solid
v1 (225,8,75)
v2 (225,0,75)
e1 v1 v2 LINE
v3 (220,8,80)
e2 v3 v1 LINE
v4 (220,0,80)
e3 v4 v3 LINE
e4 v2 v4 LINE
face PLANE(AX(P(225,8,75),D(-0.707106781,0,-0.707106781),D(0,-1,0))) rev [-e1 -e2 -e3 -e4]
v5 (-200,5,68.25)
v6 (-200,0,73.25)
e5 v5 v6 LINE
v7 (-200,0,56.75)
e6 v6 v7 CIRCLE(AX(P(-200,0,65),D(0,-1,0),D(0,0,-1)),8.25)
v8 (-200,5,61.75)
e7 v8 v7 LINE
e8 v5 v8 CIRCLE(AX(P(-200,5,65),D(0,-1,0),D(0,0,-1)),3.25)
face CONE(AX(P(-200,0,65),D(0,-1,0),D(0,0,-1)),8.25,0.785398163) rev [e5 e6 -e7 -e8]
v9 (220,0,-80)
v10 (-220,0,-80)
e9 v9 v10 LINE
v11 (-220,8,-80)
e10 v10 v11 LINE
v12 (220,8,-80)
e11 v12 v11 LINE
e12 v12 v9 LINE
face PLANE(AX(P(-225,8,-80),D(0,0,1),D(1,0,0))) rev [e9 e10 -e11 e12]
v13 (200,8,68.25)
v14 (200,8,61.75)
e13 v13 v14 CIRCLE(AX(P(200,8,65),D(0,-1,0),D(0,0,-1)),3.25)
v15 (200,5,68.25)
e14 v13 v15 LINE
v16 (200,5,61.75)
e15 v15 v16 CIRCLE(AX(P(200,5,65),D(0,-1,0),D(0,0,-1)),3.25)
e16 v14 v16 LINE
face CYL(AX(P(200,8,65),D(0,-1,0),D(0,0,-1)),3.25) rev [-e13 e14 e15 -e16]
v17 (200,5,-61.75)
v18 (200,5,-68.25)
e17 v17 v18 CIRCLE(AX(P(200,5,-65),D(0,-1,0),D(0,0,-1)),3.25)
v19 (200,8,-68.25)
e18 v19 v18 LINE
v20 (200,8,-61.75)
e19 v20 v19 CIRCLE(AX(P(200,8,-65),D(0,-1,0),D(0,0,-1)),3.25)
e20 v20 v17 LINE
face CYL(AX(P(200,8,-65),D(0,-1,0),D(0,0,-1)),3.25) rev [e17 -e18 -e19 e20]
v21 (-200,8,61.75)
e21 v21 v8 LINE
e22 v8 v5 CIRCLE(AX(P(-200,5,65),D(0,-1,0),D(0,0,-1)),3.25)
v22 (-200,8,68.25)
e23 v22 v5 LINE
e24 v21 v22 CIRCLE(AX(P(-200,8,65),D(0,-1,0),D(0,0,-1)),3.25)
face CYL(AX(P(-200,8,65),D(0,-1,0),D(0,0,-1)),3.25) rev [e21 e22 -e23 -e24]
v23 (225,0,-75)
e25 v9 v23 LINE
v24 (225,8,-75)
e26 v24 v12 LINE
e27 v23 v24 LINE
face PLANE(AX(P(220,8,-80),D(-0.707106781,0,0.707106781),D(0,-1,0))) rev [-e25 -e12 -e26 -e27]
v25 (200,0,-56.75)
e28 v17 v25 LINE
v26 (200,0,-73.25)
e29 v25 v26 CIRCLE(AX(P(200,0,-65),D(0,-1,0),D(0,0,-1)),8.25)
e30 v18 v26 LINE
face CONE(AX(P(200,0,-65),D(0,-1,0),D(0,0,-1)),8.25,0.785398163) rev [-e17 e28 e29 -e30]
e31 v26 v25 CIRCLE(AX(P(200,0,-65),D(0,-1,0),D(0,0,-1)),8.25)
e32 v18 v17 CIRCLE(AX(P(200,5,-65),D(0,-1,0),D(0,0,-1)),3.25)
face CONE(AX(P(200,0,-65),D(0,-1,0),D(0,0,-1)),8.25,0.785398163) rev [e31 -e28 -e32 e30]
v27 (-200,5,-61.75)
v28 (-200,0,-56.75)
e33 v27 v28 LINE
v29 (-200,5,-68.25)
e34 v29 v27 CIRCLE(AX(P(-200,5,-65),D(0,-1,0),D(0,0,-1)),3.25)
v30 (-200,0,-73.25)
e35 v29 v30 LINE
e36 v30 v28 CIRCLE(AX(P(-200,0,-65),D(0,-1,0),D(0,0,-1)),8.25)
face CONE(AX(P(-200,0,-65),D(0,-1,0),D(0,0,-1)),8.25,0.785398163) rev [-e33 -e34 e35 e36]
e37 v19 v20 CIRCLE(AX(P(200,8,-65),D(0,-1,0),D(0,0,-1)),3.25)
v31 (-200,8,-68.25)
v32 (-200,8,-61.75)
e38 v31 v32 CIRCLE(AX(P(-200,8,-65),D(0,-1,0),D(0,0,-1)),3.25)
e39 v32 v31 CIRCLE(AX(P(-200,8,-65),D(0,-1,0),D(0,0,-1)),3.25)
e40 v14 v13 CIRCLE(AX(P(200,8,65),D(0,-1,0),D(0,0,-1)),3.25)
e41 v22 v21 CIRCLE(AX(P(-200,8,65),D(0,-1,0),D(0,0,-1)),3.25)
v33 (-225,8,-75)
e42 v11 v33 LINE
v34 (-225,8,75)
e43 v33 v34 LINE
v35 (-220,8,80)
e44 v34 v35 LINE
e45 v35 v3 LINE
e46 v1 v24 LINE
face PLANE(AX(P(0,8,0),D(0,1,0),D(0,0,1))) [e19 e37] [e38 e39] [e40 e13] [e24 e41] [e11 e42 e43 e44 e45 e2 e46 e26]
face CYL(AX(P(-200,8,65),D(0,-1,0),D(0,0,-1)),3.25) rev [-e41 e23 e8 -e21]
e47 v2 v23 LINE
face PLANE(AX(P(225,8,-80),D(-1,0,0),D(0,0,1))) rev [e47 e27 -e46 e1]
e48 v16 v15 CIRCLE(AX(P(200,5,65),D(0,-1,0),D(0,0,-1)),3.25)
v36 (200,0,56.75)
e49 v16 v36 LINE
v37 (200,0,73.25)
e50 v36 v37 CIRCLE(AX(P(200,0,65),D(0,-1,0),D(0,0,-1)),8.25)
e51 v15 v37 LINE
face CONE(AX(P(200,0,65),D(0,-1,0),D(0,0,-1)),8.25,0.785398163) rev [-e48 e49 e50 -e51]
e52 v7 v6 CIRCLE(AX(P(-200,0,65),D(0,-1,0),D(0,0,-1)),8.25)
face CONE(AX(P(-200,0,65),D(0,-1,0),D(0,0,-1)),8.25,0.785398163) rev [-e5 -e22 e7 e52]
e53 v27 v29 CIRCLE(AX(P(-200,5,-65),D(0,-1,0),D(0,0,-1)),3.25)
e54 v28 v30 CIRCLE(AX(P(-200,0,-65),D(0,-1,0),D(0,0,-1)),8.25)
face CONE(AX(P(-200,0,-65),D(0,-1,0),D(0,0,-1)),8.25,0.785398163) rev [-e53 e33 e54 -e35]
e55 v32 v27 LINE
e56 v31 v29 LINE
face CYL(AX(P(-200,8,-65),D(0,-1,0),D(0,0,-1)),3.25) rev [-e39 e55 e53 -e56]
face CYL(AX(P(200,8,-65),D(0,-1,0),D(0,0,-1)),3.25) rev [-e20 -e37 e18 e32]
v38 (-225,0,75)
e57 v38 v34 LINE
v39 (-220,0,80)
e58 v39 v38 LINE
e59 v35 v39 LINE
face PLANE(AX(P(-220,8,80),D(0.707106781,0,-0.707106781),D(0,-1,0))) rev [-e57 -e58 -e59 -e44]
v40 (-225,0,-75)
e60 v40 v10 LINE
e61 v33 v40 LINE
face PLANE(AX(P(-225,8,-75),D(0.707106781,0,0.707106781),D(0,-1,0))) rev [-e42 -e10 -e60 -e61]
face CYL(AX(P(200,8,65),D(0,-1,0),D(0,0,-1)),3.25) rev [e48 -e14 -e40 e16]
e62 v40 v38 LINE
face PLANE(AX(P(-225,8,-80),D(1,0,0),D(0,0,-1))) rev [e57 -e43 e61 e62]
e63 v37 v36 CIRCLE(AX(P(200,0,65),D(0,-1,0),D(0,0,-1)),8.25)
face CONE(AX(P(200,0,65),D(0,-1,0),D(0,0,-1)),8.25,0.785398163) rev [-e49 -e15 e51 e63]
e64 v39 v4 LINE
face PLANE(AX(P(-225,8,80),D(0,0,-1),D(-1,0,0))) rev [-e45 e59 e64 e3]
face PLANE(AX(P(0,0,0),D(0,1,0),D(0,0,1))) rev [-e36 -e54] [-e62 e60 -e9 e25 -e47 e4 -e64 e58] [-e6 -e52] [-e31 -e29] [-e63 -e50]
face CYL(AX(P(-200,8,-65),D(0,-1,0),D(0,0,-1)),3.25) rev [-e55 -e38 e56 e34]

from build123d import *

# Parameters (mm, degrees)
SKETCH1_W                    = 450
SKETCH1_H                    = 160
BOSS_EXTRUDE1_DEPTH          = 8
SKETCH15_R                   = 3.25
CUT_EXTRUDE5_DEPTH           = 8
SKETCH16_R                   = 8.25
CUT_EXTRUDE6_DEPTH           = 5
CUT_EXTRUDE6_DRAFT           = -45
CUT_EXTRUDE6_PROFILE_2_DEPTH = 5
CUT_EXTRUDE6_PROFILE_2_DRAFT = -45
CUT_EXTRUDE6_PROFILE_3_DEPTH = 5
CUT_EXTRUDE6_PROFILE_3_DRAFT = -45
CUT_EXTRUDE6_PROFILE_4_DEPTH = 5
CUT_EXTRUDE6_PROFILE_4_DRAFT = -45
CHAMFER1_SIZE                = 5


with BuildPart() as part:
    # Sketch1 → Boss-Extrude1 (new body)
    with BuildSketch(Plane(origin=(0, 0, 0), x_dir=(1, 0, 0), z_dir=(0, 1, 0))):
        Rectangle(SKETCH1_W, SKETCH1_H)
    extrude(amount=BOSS_EXTRUDE1_DEPTH)

    # Sketch15 → Cut-Extrude5 (cut)
    with BuildSketch(Plane.XZ):
        with Locations(Location((-200, 65, 0), (0, 0, 270))):
            Circle(SKETCH15_R)
        with Locations(Location((-200, -65, 0), (0, 0, 270))):
            Circle(SKETCH15_R)
        with Locations(Location((200, 65, 0), (0, 0, 270))):
            Circle(SKETCH15_R)
        with Locations(Location((200, -65, 0), (0, 0, 270))):
            Circle(SKETCH15_R)
    extrude(amount=-CUT_EXTRUDE5_DEPTH, mode=Mode.SUBTRACT)


with BuildPart() as cut_extrude6_tool:
    # Sketch16 → Cut-Extrude6 (with draft: the straight prism first)
    with BuildSketch(Plane.XZ):
        with Locations((-200, 65)):
            Circle(SKETCH16_R)
    extrude(amount=-CUT_EXTRUDE6_DEPTH)
    # Cut-Extrude6: the draft: its side faces are tilted about the plane it starts from
    cut_extrude6_sides = [cut_extrude6_tool.faces().sort_by_distance(p)[0] for p in [
        (-208.25, 2.5, 65),
    ]]
    draft(cut_extrude6_sides, Plane.XZ, CUT_EXTRUDE6_DRAFT)


with BuildPart() as part_1:
    add(part.part)

    # Cut-Extrude6: cut by cut_extrude6_tool
    add(cut_extrude6_tool.part, mode=Mode.SUBTRACT)


with BuildPart() as cut_extrude6_profile_2_tool:
    # Sketch16 → Cut-Extrude6 profile 2 (with draft: the straight prism first)
    with BuildSketch(Plane.XZ):
        with Locations((-200, -65)):
            Circle(SKETCH16_R)
    extrude(amount=-CUT_EXTRUDE6_PROFILE_2_DEPTH)
    # Cut-Extrude6 profile 2: the draft: its side faces are tilted about the plane it starts from
    cut_extrude6_profile_2_sides = [cut_extrude6_profile_2_tool.faces().sort_by_distance(p)[0] for p in [
        (-208.25, 2.5, -65),
    ]]
    draft(cut_extrude6_profile_2_sides, Plane.XZ, CUT_EXTRUDE6_PROFILE_2_DRAFT)


with BuildPart() as part_2:
    add(part_1.part)

    # Cut-Extrude6 profile 2: cut by cut_extrude6_profile_2_tool
    add(cut_extrude6_profile_2_tool.part, mode=Mode.SUBTRACT)


with BuildPart() as cut_extrude6_profile_3_tool:
    # Sketch16 → Cut-Extrude6 profile 3 (with draft: the straight prism first)
    with BuildSketch(Plane.XZ):
        with Locations((200, 65)):
            Circle(SKETCH16_R)
    extrude(amount=-CUT_EXTRUDE6_PROFILE_3_DEPTH)
    # Cut-Extrude6 profile 3: the draft: its side faces are tilted about the plane it starts from
    cut_extrude6_profile_3_sides = [cut_extrude6_profile_3_tool.faces().sort_by_distance(p)[0] for p in [
        (191.75, 2.5, 65),
    ]]
    draft(cut_extrude6_profile_3_sides, Plane.XZ, CUT_EXTRUDE6_PROFILE_3_DRAFT)


with BuildPart() as part_3:
    add(part_2.part)

    # Cut-Extrude6 profile 3: cut by cut_extrude6_profile_3_tool
    add(cut_extrude6_profile_3_tool.part, mode=Mode.SUBTRACT)


with BuildPart() as cut_extrude6_profile_4_tool:
    # Sketch16 → Cut-Extrude6 profile 4 (with draft: the straight prism first)
    with BuildSketch(Plane.XZ):
        with Locations((200, -65)):
            Circle(SKETCH16_R)
    extrude(amount=-CUT_EXTRUDE6_PROFILE_4_DEPTH)
    # Cut-Extrude6 profile 4: the draft: its side faces are tilted about the plane it starts from
    cut_extrude6_profile_4_sides = [cut_extrude6_profile_4_tool.faces().sort_by_distance(p)[0] for p in [
        (191.75, 2.5, -65),
    ]]
    draft(cut_extrude6_profile_4_sides, Plane.XZ, CUT_EXTRUDE6_PROFILE_4_DRAFT)


with BuildPart() as part_4:
    add(part_3.part)

    # Cut-Extrude6 profile 4: cut by cut_extrude6_profile_4_tool
    add(cut_extrude6_profile_4_tool.part, mode=Mode.SUBTRACT)

    # Chamfer1
    chamfer1_edges = [part_4.edges().sort_by_distance(p)[0] for p in [
        (225, 4, 80),
        (-225, 4, 80),
        (-225, 4, -80),
        (225, 4, -80),
    ]]
    chamfer(chamfer1_edges, length=CHAMFER1_SIZE)


solid = part_4.part
